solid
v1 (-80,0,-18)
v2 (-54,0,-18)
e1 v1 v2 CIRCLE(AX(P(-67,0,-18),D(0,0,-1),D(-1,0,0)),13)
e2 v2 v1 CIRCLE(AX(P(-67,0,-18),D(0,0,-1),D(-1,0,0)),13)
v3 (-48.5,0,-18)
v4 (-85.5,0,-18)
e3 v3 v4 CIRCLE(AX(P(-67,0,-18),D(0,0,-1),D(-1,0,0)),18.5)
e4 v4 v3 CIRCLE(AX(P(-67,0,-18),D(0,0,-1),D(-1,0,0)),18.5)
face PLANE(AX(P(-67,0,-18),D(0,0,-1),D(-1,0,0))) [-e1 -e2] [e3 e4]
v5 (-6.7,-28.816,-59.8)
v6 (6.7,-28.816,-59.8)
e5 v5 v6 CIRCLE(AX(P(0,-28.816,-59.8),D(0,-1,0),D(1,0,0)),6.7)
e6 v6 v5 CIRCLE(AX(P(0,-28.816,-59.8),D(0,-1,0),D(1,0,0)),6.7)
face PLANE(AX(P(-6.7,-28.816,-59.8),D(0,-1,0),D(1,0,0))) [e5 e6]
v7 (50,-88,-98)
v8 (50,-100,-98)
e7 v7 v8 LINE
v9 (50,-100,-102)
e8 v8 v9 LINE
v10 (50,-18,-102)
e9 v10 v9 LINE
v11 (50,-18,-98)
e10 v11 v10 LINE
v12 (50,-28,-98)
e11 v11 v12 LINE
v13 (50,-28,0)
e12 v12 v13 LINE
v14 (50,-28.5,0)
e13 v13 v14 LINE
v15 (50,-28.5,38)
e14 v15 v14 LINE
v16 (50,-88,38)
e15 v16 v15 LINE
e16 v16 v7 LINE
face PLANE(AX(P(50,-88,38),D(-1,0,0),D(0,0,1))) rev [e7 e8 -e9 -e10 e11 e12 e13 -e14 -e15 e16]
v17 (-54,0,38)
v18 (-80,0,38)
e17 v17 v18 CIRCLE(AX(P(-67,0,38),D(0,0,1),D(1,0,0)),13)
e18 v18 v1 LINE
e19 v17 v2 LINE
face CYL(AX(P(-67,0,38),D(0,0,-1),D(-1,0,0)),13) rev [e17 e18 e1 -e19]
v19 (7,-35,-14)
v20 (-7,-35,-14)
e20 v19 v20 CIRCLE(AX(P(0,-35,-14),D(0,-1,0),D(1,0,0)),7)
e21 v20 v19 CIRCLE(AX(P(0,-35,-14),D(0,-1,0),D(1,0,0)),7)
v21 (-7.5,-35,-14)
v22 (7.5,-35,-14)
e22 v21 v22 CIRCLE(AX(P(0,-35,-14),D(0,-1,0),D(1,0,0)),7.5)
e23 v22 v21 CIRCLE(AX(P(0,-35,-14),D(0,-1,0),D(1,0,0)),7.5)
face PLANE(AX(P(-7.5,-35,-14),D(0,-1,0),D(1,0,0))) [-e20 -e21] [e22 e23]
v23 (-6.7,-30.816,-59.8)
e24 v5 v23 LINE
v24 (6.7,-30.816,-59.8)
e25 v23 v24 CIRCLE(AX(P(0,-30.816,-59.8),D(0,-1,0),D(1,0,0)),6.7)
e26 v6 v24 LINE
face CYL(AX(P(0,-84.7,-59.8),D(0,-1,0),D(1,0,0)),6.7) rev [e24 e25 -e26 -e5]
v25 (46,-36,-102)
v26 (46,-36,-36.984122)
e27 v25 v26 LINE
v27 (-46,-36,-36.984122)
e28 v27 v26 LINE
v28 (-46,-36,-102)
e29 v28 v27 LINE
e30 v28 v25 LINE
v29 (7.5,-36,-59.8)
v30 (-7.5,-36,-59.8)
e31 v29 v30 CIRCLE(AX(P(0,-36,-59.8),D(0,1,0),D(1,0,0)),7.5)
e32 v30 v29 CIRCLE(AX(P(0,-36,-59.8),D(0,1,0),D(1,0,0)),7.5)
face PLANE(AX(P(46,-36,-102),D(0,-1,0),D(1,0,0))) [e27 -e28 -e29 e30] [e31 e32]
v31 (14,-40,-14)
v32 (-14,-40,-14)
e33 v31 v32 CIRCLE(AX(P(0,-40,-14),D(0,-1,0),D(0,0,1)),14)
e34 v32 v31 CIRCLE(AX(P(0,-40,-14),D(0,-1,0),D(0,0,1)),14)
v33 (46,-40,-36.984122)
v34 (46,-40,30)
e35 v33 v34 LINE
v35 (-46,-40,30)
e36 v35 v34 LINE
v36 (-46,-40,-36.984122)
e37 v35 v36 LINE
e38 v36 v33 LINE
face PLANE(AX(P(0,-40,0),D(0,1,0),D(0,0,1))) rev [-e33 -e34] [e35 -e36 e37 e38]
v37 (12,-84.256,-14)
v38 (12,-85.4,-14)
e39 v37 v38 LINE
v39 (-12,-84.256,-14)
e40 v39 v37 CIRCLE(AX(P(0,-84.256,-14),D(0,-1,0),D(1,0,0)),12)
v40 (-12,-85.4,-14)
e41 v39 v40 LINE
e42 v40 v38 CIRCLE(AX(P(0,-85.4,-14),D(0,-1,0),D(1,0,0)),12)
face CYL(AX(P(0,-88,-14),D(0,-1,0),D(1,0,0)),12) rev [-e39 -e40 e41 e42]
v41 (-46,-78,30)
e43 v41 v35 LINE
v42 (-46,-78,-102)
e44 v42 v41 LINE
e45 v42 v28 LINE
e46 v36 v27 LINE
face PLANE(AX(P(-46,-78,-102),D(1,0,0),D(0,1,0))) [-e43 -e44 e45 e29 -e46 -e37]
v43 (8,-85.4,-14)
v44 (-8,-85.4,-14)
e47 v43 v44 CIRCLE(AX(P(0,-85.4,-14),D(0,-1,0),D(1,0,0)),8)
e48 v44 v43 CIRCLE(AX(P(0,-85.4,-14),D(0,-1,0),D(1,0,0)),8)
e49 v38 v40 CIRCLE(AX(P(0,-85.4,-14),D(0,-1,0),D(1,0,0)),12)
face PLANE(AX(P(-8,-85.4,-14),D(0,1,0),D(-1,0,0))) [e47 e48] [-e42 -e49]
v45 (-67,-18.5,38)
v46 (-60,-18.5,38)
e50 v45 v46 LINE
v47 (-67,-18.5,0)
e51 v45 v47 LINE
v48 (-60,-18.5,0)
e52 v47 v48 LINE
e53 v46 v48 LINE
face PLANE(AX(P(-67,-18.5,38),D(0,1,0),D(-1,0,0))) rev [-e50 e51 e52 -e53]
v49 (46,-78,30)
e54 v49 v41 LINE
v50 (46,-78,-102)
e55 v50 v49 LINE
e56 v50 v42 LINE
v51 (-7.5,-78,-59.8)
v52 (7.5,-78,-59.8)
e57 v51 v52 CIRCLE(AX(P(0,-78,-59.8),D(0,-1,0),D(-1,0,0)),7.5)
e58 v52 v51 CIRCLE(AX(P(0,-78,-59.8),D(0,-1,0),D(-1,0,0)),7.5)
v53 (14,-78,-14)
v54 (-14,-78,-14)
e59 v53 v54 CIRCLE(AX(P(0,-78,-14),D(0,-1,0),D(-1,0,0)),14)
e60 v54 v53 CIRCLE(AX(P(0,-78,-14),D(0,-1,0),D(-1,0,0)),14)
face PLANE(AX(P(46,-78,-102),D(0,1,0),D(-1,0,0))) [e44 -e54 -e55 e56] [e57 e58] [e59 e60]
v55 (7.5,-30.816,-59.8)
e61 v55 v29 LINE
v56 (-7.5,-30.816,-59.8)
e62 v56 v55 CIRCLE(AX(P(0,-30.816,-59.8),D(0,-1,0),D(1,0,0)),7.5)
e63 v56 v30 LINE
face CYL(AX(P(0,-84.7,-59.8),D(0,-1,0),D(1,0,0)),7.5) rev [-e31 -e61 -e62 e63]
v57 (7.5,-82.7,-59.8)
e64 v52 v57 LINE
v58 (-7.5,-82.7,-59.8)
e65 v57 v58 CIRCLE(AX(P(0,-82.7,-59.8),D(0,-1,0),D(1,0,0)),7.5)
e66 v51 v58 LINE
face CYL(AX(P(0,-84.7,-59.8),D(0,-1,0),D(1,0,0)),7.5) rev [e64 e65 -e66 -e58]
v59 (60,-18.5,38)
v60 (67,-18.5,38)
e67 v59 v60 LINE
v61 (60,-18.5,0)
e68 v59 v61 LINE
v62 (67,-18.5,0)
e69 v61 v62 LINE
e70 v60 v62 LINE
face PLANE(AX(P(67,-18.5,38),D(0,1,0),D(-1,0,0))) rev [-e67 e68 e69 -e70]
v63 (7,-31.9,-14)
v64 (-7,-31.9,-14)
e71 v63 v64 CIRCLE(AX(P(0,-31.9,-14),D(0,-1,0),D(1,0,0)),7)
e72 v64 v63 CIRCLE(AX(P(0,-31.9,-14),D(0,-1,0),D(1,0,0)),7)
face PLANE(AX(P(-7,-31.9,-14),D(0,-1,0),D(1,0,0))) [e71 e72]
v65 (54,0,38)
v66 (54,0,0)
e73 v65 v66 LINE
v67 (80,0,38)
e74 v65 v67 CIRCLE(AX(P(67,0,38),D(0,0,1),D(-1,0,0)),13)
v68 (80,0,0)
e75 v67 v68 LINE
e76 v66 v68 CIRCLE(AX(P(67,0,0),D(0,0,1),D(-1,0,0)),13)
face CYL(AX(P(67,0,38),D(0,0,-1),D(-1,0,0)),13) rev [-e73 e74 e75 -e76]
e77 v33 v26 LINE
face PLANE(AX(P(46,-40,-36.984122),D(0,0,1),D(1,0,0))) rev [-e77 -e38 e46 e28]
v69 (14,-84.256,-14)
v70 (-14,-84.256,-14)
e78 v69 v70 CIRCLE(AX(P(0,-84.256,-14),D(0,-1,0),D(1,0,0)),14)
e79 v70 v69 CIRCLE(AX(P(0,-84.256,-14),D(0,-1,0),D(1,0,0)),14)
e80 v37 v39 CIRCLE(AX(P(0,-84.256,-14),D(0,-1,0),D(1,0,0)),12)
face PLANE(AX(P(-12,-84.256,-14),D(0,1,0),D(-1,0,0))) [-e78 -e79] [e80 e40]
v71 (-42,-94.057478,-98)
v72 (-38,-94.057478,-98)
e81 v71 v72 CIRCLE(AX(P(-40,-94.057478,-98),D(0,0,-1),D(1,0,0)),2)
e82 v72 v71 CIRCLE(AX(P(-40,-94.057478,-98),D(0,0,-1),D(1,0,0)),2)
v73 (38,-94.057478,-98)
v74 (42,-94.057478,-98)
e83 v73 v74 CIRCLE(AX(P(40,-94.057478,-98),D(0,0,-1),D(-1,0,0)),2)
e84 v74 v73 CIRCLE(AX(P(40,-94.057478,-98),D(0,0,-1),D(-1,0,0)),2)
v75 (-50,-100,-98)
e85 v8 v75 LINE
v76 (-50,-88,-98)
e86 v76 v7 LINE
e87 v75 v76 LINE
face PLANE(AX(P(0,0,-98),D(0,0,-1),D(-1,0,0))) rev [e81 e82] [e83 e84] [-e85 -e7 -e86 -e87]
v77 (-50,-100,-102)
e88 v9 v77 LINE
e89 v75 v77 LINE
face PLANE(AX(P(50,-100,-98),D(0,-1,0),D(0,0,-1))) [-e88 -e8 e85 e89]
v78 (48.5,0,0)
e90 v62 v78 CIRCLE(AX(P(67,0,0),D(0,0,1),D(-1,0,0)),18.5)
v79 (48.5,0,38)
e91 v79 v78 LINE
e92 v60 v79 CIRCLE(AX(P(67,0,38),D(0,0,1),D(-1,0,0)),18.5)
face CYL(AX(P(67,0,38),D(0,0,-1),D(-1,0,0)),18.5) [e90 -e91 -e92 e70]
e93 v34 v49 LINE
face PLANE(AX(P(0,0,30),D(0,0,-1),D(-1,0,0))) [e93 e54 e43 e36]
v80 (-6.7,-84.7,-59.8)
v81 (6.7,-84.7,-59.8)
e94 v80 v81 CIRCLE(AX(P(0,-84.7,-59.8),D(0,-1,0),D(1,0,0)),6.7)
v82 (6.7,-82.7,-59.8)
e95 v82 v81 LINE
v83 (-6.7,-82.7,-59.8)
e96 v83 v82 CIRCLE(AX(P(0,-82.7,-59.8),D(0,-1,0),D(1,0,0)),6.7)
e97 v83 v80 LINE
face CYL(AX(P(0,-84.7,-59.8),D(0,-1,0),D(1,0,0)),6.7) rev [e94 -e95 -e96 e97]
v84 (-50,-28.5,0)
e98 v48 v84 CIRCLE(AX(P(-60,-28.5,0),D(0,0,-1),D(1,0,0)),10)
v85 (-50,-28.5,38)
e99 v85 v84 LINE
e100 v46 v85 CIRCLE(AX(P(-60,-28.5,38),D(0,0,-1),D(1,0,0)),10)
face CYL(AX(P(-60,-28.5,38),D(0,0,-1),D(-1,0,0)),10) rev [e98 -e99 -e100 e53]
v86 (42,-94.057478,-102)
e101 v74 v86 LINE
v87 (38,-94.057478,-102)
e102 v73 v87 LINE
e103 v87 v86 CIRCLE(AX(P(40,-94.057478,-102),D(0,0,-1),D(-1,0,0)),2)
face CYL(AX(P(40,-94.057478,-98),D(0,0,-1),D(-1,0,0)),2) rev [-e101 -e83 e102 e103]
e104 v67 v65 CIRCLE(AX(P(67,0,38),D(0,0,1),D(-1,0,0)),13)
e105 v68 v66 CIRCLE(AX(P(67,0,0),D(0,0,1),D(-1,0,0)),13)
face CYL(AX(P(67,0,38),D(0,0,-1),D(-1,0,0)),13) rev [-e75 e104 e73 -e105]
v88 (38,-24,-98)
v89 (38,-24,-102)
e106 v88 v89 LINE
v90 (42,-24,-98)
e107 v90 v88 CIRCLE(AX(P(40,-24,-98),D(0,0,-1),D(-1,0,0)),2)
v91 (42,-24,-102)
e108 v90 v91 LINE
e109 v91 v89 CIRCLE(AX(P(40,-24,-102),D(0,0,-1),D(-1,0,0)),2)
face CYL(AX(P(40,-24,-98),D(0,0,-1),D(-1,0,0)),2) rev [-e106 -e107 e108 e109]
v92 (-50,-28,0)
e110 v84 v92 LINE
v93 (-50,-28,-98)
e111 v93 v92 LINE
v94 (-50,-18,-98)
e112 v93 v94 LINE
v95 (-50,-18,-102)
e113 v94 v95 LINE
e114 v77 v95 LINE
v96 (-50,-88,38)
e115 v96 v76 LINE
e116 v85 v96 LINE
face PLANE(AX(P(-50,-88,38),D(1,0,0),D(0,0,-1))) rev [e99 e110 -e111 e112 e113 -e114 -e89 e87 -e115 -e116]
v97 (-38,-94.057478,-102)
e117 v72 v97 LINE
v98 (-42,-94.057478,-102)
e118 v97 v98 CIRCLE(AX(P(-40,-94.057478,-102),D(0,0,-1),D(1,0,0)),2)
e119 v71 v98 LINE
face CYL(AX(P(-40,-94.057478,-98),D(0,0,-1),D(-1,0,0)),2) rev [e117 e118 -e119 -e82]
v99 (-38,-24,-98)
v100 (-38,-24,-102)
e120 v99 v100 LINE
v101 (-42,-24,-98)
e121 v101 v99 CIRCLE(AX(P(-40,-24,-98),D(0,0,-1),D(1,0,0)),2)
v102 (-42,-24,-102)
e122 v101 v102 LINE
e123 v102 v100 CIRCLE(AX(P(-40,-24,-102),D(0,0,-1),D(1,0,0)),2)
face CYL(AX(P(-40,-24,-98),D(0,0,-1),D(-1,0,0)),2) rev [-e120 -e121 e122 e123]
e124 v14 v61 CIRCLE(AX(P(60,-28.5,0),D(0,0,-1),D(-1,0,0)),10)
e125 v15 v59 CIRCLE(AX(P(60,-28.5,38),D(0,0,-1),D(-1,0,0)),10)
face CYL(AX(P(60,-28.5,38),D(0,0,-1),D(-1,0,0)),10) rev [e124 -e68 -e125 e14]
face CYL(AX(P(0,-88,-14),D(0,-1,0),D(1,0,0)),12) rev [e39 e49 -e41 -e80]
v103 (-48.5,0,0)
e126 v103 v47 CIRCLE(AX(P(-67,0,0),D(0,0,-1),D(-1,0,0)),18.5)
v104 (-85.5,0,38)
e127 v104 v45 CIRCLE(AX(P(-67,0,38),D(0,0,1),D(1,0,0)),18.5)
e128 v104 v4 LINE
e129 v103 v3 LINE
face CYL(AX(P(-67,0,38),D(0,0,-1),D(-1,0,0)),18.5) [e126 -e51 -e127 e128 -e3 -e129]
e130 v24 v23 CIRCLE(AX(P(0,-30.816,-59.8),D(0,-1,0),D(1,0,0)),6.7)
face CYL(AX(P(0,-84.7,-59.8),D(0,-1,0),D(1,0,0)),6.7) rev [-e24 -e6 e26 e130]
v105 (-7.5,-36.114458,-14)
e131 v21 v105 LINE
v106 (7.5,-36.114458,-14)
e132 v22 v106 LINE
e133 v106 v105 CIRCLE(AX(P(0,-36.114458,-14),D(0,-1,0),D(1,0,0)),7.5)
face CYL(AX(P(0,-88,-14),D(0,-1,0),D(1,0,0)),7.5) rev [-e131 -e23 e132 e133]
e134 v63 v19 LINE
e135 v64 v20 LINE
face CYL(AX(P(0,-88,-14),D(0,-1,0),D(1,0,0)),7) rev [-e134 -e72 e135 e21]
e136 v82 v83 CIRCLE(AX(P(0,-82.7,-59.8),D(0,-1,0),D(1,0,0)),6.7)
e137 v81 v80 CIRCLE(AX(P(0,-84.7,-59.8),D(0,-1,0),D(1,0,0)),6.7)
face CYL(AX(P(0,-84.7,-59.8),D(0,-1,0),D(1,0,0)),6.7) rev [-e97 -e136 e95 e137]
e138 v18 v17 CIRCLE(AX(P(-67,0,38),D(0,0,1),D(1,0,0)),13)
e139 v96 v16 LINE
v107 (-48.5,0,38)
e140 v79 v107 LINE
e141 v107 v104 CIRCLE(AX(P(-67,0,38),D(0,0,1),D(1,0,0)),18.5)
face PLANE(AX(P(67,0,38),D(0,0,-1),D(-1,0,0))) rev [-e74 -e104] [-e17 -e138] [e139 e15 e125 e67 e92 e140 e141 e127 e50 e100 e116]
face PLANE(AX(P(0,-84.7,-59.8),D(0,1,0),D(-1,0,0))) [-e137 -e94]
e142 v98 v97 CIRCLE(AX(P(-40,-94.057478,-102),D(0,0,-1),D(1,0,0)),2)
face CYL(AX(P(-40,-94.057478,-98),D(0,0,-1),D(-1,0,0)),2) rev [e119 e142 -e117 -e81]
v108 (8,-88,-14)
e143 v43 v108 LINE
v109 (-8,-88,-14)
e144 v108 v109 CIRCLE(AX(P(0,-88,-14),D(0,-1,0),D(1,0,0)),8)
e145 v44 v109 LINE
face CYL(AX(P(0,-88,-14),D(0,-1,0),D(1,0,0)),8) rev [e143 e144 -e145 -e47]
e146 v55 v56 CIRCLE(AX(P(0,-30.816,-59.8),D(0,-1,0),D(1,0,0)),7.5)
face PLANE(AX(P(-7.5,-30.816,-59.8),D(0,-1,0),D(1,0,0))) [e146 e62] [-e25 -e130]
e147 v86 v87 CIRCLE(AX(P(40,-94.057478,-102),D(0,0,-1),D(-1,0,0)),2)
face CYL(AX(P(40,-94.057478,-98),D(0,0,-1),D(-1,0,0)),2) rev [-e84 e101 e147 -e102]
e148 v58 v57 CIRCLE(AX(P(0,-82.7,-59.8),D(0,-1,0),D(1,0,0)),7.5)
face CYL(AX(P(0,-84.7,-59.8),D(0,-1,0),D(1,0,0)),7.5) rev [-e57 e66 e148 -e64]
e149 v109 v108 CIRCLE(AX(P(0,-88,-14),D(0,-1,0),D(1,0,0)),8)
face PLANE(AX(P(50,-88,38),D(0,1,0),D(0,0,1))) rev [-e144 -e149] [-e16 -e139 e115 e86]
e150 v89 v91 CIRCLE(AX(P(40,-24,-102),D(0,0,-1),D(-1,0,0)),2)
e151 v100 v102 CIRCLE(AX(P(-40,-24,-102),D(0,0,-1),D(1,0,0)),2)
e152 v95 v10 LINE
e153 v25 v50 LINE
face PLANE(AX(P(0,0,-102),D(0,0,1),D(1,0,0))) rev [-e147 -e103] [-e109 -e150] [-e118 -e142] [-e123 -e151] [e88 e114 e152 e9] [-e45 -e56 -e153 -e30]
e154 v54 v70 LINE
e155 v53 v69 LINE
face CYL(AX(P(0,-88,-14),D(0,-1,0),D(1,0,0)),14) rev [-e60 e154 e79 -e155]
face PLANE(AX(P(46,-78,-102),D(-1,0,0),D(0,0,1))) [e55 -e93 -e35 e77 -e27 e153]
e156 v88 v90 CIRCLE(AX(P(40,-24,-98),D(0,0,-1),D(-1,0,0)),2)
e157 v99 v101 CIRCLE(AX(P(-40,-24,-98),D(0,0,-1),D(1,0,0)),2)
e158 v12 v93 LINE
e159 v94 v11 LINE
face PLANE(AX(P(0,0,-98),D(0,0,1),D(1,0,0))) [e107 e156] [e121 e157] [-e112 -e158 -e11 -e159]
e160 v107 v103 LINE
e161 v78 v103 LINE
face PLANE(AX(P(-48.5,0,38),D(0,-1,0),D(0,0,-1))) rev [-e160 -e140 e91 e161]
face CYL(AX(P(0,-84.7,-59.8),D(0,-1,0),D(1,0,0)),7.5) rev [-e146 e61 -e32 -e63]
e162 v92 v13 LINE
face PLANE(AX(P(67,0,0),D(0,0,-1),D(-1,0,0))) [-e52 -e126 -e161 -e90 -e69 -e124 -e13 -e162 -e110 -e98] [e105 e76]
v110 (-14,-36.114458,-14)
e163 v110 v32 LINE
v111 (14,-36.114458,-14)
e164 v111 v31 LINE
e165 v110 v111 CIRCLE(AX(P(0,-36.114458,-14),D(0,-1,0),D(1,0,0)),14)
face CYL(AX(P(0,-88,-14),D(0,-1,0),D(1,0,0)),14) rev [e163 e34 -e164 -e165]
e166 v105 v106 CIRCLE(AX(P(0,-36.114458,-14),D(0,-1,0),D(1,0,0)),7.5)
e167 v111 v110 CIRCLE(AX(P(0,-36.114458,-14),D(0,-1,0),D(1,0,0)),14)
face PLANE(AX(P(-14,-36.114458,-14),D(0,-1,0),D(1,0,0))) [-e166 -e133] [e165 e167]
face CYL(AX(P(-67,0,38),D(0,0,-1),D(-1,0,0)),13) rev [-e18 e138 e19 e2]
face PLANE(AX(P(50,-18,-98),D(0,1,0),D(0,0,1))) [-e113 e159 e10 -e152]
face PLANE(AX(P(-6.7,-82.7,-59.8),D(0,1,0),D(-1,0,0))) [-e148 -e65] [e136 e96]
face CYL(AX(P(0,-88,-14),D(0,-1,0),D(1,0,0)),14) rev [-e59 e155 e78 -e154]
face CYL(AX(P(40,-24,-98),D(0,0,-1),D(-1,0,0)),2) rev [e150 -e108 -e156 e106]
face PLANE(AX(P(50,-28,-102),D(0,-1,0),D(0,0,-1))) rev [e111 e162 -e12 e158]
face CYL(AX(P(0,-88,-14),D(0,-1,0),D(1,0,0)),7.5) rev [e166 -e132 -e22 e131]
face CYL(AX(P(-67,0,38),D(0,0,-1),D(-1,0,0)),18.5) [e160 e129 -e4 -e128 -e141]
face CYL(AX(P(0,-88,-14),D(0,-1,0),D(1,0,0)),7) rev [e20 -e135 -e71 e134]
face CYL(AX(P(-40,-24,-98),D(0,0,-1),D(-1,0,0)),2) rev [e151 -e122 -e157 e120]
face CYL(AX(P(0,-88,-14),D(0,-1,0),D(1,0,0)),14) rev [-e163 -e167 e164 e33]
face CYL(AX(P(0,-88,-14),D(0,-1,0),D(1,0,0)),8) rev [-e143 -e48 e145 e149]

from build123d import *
from build123d.topology import SkipClean

# Parameters (mm, degrees)
SKETCH_2_R          = 13
EXTRUDE_1_DEPTH     = 38
SKETCH_23_W         = 100
SKETCH_23_H         = 60
SKETCH_23_W_2       = 92
SKETCH_23_H_2       = 42
EXTRUDE_7_DEPTH     = 102
SKETCH_25_R         = 7
CUT_EXTRUDE_4_DEPTH = 50
EXTRUDE_START       = 18
SKETCH_26_R         = 18.5
SKETCH_26_R_2       = 13
EXTRUDE_8_DEPTH     = 18
SKETCH_28_W         = 92
SKETCH_28_H         = 42
CUT_EXTRUDE_5_DEPTH = 30
SKETCH_29_W         = 92
SKETCH_29_H         = 67
EXTRUDE_9_DEPTH     = 4
SKETCH_32_W         = 100
SKETCH_32_H         = 10
SKETCH_32_H_2       = 12
EXTRUDE_10_DEPTH    = 4
SKETCH_33_R         = 2
CUT_EXTRUDE_6_DEPTH = 4


with BuildPart() as part:
    # 草图2 → 凸台-拉伸1 (new body)
    with BuildSketch(Plane.XY):
        with BuildLine():
            Line((-48.5, 0), (48.5, 0))
            ThreePointArc((48.5, 0), (80.081475452, 13.081475452), (67, -18.5))
            Line((67, -18.5), (60, -18.5))
            ThreePointArc((60, -18.5), (52.928932188, -21.428932188), (50, -28.5))
            Line((50, -28.5), (50, -88))
            Line((50, -88), (-50, -88))
            Line((-50, -88), (-50, -28.5))
            ThreePointArc((-50, -28.5), (-52.928932188, -21.428932188), (-60, -18.5))
            Line((-60, -18.5), (-67, -18.5))
            ThreePointArc((-67, -18.5), (-80.081475452, 13.081475452), (-48.5, 0))
        make_face()
        with Locations((-67, 0)):
            Circle(SKETCH_2_R, mode=Mode.SUBTRACT)
        with Locations(Location((67, 0, 0), (0, 0, 180))):
            Circle(SKETCH_2_R, mode=Mode.SUBTRACT)
    extrude(amount=EXTRUDE_1_DEPTH)

    # 草图23 → 凸台-拉伸7 (add)
    with BuildSketch(Plane(origin=(0, 0, 0), x_dir=(-1, 0, 0), z_dir=(0, 0, -1))):
        with Locations((0, -58)):
            Rectangle(SKETCH_23_W, SKETCH_23_H)
        with Locations((0, -57)):
            Rectangle(SKETCH_23_W_2, SKETCH_23_H_2, mode=Mode.SUBTRACT)
    extrude(amount=EXTRUDE_7_DEPTH)

    # 草图25 → 切除-拉伸4 (cut)
    with BuildSketch(Plane(origin=(0, -88, 0), x_dir=(-1, 0, 0), z_dir=(0, -1, 0))):
        with Locations(Location((0, 14, 0), (0, 0, 90))):
            Circle(SKETCH_25_R)
    extrude(amount=-CUT_EXTRUDE_4_DEPTH, mode=Mode.SUBTRACT)

    # 草图26 → 凸台-拉伸8 (add)
    with SkipClean():  # the faces are left unmerged after this step: merging them gives an invalid solid
        with BuildSketch(Plane(origin=(0, 0, 0), x_dir=(-1, 0, 0), z_dir=(0, 0, -1)).offset(EXTRUDE_START)):
            with Locations((67, 0)):
                Circle(SKETCH_26_R)
            with Locations((67, 0)):
                Circle(SKETCH_26_R_2, mode=Mode.SUBTRACT)
        extrude(amount=-EXTRUDE_8_DEPTH)

    # 草图28 → 切除-拉伸5 (cut)
    with SkipClean():  # the faces are left unmerged after this step: merging them gives an invalid solid
        with BuildSketch(Plane(origin=(0, 0, 0), x_dir=(-1, 0, 0), z_dir=(0, 0, -1))):
            with Locations((0, -57)):
                Rectangle(SKETCH_28_W, SKETCH_28_H)
        extrude(amount=-CUT_EXTRUDE_5_DEPTH, mode=Mode.SUBTRACT)

    # 草图29 → 凸台-拉伸9 (add)
    with SkipClean():  # the faces are left unmerged after this step: merging them gives an invalid solid
        with BuildSketch(Plane(origin=(0, -36, 0), x_dir=(-1, 0, 0), z_dir=(0, -1, 0))):
            with Locations((0, 3.48412197)):
                Rectangle(SKETCH_29_W, SKETCH_29_H)
        extrude(amount=EXTRUDE_9_DEPTH)

    # 草图30 → 切除-旋转3 (revolve, cut)
    with SkipClean():  # the faces are left unmerged after this step: merging them gives an invalid solid
        with BuildSketch(Plane.XY.offset(-14), mode=Mode.PRIVATE) as cut_revolve_3_sk:
            Polygon((0, -88), (-8, -88), (-8, -85.4), (-12, -85.4), (-12, -84.256), (-14, -84.256), (-14, -36.11445811), (-7.5, -36.11445811), (-7.5, -35), (-7, -35), (-7, -31.9), (0, -31.9), align=None)
        revolve(cut_revolve_3_sk.sketch.rotate(Axis((0, -88, -14), (0, 1, 0)), 180), axis=Axis((0, -88, -14), (0, 1, 0)), mode=Mode.SUBTRACT)

    # 草图31 → 切除-旋转4 (revolve, cut)
    with SkipClean():  # the faces are left unmerged after this step: merging them gives an invalid solid
        with BuildSketch(Plane.XY.offset(-59.8), mode=Mode.PRIVATE) as cut_revolve_4_sk:
            Polygon((0, -84.7), (-6.7, -84.7), (-6.7, -82.7), (-7.5, -82.7), (-7.5, -30.816), (-6.7, -30.816), (-6.7, -28.816), (0, -28.816), align=None)
        revolve(cut_revolve_4_sk.sketch.rotate(Axis((0, -84.7, -59.8), (0, 1, 0)), 180), axis=Axis((0, -84.7, -59.8), (0, 1, 0)), mode=Mode.SUBTRACT)

    # 草图32 → 凸台-拉伸10 (add)
    with SkipClean():  # the faces are left unmerged after this step: merging them gives an invalid solid
        with BuildSketch(Plane(origin=(0, 0, -102), x_dir=(-1, 0, 0), z_dir=(0, 0, -1))):
            with Locations((0, -23)):
                Rectangle(SKETCH_32_W, SKETCH_32_H)
            with Locations((0, -94)):
                Rectangle(SKETCH_32_W, SKETCH_32_H_2)
        extrude(amount=-EXTRUDE_10_DEPTH)

    # 草图33 → 切除-拉伸6 (cut)
    with SkipClean():  # the faces are left unmerged after this step: merging them gives an invalid solid
        with BuildSketch(Plane(origin=(0, 0, -102), x_dir=(-1, 0, 0), z_dir=(0, 0, -1))):
            with Locations((-40, -94.057478358)):
                Circle(SKETCH_33_R)
            with Locations((-40, -24)):
                Circle(SKETCH_33_R)
            with Locations(Location((40, -94.057478358, 0), (0, 0, 180))):
                Circle(SKETCH_33_R)
            with Locations(Location((40, -24, 0), (0, 0, 180))):
                Circle(SKETCH_33_R)
        extrude(amount=-CUT_EXTRUDE_6_DEPTH, mode=Mode.SUBTRACT)


solid = part.part
